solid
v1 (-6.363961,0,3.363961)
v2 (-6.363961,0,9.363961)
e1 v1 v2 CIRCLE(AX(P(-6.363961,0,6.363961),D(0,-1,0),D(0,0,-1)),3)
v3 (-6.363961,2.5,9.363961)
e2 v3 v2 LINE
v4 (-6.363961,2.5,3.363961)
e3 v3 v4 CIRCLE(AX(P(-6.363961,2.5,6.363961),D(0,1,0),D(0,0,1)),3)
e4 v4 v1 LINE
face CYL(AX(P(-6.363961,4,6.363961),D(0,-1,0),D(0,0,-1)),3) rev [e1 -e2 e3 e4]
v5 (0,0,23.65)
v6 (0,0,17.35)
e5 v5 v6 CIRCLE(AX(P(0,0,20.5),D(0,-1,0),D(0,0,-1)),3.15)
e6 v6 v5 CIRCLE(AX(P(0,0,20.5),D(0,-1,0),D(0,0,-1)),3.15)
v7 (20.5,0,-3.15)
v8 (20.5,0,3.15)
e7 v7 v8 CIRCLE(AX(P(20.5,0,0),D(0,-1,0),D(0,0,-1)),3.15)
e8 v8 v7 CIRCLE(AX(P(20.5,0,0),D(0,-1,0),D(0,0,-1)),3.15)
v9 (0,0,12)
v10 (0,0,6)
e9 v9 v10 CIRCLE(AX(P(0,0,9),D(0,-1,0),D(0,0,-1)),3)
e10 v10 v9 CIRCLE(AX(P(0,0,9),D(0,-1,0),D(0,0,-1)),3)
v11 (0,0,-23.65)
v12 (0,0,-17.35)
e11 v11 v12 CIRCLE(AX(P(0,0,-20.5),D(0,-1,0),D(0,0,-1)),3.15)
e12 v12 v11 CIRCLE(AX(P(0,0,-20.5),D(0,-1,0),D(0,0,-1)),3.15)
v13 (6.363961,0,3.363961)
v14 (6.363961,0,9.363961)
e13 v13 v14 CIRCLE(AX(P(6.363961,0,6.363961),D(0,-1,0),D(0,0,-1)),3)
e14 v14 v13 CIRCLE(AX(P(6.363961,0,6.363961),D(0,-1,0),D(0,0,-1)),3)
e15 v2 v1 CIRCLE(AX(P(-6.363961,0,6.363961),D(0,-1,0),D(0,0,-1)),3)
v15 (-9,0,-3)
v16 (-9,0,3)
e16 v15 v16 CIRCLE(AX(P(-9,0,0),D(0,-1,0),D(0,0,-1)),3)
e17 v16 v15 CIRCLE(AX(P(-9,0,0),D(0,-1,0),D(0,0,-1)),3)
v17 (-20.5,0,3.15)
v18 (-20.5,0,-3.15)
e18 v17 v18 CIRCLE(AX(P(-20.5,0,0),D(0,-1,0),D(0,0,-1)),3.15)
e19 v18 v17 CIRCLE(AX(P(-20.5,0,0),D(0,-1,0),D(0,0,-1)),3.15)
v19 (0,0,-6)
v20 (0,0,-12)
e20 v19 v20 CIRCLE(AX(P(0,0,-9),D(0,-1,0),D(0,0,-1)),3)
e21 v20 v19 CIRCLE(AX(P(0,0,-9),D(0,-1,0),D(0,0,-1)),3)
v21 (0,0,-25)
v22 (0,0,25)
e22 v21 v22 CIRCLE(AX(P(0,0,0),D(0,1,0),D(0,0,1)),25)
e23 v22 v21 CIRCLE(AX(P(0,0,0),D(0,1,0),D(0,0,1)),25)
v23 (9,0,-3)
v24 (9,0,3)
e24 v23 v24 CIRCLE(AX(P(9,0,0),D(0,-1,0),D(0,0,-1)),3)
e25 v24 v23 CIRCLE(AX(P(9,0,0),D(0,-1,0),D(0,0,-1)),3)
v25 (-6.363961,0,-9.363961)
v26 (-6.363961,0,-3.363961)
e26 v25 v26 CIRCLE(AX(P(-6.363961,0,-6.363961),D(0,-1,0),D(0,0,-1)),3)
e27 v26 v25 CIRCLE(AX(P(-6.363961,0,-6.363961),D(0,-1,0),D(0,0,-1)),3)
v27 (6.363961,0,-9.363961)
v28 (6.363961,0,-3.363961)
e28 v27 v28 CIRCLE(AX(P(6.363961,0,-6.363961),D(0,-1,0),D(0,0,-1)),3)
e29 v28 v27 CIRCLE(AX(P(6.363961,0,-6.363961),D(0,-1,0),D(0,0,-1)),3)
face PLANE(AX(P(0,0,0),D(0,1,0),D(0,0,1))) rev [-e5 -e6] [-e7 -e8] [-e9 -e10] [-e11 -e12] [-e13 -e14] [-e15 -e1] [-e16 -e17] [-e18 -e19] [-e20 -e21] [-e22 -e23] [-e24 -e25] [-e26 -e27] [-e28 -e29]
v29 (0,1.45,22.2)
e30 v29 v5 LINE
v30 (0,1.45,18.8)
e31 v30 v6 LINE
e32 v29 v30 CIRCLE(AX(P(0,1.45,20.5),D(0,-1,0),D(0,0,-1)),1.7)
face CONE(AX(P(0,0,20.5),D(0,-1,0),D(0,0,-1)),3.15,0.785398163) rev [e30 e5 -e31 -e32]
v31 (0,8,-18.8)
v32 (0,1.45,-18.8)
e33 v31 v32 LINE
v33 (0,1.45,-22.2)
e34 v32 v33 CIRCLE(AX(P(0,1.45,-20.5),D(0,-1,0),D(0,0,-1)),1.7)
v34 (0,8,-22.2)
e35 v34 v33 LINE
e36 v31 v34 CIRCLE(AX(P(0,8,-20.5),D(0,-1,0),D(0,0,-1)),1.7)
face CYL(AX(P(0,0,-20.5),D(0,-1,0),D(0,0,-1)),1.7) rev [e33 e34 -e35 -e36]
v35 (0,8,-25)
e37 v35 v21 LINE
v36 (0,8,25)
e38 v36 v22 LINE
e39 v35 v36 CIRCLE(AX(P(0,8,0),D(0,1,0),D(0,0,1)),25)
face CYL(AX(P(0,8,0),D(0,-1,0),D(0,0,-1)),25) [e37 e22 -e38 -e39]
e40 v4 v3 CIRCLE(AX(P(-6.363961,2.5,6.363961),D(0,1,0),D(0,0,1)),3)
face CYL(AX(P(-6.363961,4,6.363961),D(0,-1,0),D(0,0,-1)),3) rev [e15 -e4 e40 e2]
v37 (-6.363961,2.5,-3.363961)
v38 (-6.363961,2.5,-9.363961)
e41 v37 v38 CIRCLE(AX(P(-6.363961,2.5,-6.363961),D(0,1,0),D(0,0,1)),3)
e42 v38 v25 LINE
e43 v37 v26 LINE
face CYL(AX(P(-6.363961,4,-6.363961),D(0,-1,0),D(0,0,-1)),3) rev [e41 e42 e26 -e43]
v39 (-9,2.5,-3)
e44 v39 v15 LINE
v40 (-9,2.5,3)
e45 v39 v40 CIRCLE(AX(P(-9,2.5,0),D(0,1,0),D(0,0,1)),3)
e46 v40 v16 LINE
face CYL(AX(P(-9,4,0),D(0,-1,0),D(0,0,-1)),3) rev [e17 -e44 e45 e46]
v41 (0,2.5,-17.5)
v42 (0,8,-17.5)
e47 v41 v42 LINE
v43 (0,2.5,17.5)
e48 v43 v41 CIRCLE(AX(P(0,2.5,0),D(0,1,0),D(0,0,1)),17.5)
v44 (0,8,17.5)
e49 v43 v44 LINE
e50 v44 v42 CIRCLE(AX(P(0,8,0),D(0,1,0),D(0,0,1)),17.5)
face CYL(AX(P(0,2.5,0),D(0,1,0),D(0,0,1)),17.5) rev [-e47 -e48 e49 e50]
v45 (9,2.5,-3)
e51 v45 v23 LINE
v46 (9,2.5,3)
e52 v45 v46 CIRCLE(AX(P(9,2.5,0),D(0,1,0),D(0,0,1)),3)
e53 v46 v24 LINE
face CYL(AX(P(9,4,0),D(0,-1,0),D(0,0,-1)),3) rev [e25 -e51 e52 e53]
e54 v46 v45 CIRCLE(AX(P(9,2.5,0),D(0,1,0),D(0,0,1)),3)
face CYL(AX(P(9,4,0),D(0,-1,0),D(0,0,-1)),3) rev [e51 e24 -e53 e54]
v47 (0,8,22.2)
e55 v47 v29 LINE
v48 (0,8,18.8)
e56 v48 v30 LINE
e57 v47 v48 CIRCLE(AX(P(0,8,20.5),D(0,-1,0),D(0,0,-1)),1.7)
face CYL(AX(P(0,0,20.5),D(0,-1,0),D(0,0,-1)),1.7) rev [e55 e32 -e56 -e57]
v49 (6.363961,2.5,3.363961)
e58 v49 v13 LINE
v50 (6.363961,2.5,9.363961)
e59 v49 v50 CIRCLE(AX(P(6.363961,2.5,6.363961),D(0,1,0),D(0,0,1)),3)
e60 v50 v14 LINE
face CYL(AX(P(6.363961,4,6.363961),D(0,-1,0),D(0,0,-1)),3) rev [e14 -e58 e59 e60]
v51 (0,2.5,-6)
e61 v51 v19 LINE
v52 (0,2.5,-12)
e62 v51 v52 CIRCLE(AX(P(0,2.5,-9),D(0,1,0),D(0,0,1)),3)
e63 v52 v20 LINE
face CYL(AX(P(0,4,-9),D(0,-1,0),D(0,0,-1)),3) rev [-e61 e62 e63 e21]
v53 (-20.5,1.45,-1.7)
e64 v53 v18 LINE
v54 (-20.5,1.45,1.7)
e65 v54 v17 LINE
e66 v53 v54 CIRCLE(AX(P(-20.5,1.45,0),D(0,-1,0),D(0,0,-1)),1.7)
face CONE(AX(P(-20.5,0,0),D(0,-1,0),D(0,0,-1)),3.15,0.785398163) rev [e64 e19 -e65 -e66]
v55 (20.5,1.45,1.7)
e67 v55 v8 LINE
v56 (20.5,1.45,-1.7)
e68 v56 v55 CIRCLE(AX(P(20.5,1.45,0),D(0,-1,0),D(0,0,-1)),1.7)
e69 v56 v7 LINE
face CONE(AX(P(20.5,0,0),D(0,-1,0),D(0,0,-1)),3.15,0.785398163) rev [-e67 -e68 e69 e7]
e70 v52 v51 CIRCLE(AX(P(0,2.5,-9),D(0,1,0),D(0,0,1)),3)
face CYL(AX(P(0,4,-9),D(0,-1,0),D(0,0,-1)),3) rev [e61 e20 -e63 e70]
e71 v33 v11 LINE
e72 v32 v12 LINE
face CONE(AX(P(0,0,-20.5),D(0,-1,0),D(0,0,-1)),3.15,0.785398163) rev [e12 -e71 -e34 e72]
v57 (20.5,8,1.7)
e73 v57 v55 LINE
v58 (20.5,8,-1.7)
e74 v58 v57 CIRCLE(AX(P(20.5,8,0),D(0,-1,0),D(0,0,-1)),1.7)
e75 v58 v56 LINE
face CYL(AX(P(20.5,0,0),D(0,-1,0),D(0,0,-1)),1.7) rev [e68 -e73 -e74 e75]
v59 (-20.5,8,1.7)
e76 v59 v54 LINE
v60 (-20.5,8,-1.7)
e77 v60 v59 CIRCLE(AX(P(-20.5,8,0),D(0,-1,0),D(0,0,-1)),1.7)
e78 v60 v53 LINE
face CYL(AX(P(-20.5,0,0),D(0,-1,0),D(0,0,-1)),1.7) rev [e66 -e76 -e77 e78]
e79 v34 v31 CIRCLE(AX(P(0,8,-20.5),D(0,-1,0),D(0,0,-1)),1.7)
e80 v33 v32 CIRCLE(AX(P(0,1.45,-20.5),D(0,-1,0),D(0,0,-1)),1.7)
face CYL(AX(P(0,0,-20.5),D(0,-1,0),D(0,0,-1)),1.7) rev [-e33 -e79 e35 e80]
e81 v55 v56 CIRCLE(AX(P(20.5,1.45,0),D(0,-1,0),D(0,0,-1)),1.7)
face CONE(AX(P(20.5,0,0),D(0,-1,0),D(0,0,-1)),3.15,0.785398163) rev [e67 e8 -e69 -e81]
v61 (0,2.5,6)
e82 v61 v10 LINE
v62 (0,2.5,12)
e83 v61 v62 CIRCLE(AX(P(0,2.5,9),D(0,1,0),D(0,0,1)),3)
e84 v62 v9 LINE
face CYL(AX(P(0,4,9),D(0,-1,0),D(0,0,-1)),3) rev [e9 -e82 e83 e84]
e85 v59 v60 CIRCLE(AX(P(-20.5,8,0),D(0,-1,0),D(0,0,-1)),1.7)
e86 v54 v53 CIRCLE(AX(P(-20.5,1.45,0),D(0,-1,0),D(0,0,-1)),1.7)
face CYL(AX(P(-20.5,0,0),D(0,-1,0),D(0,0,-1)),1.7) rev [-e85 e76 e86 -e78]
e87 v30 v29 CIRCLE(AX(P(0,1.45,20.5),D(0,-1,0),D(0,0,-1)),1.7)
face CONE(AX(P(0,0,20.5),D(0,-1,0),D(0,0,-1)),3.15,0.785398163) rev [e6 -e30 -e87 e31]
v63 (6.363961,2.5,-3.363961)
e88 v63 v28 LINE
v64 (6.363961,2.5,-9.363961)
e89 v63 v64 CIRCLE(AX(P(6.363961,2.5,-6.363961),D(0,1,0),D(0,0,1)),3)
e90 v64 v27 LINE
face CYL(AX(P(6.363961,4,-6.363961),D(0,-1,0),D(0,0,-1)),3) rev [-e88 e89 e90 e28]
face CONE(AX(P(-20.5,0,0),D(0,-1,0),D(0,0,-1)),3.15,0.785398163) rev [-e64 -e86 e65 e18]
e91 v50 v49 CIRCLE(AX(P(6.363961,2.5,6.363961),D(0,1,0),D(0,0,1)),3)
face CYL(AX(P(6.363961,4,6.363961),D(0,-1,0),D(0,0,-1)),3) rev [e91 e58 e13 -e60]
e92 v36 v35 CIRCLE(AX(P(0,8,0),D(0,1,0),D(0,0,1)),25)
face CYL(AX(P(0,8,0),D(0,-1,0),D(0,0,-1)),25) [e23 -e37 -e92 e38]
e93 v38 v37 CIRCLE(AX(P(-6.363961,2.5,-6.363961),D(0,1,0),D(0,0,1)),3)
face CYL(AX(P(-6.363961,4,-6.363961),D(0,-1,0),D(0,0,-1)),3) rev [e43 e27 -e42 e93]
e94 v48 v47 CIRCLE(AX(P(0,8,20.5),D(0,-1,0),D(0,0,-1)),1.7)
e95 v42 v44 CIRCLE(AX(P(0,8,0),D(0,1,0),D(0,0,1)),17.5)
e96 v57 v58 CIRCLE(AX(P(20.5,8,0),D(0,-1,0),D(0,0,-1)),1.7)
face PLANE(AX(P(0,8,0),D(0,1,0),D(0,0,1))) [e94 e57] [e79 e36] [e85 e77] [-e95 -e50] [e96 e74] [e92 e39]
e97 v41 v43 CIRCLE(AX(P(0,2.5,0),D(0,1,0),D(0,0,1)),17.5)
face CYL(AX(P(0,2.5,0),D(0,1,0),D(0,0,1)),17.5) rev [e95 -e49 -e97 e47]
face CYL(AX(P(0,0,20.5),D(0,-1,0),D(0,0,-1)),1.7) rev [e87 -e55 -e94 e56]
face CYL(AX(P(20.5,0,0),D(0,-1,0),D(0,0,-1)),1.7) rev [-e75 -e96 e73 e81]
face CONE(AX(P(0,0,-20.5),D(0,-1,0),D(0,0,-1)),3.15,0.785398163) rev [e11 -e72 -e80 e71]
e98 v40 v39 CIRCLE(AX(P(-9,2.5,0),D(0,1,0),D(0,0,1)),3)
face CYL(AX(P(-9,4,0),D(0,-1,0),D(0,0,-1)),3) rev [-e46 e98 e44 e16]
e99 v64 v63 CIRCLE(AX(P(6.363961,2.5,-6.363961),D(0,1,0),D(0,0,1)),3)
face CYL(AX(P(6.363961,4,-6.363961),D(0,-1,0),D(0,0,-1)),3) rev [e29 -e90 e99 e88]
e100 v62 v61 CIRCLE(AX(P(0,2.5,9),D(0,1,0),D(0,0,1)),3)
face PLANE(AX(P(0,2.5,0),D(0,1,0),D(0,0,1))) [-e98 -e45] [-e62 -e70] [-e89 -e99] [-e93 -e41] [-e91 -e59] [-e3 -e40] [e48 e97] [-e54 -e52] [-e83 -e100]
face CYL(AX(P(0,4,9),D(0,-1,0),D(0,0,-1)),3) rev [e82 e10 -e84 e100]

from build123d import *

# Parameters (mm, degrees)
SKETCH1_R                                       = 25
BOSS_EXTRUDE1_DEPTH                             = 8
SKETCH2_R                                       = 17.5
CUT_EXTRUDE1_DEPTH                              = 5.5
SKETCH3_R                                       = 3
CUT_EXTRUDE2_DEPTH                              = 4
CSK_FOR_M3_FLAT_HEAD_MACHINE_SCREW1_D           = 3.4
CSK_FOR_M3_FLAT_HEAD_MACHINE_SCREW1_CSINK_D     = 6.3
CSK_FOR_M3_FLAT_HEAD_MACHINE_SCREW1_CSINK_ANGLE = 90


with BuildPart() as part:
    # Sketch1 → Boss-Extrude1 (new body)
    with BuildSketch(Plane(origin=(0, 0, 0), x_dir=(1, 0, 0), z_dir=(0, 1, 0))):
        with Locations(Location((0, 0, 0), (0, 0, 270))):
            Circle(SKETCH1_R)
    extrude(amount=BOSS_EXTRUDE1_DEPTH)

    # Sketch2 → Cut-Extrude1 (cut)
    with BuildSketch(Plane(origin=(0, 8, 0), x_dir=(1, 0, 0), z_dir=(0, 1, 0))):
        with Locations(Location((0, 0, 0), (0, 0, 270))):
            Circle(SKETCH2_R)
    extrude(amount=-CUT_EXTRUDE1_DEPTH, mode=Mode.SUBTRACT)

    # Sketch3 → Cut-Extrude2 (cut)
    with BuildSketch(Plane.XZ):
        with Locations(Location((0, -9, 0), (0, 0, 270))):
            Circle(SKETCH3_R)
        with Locations(Location((-6.363961031, -6.363961031, 0), (0, 0, 270))):
            Circle(SKETCH3_R)
        with Locations(Location((-9, 0, 0), (0, 0, 270))):
            Circle(SKETCH3_R)
        with Locations(Location((-6.363961031, 6.363961031, 0), (0, 0, 270))):
            Circle(SKETCH3_R)
        with Locations(Location((0, 9, 0), (0, 0, 270))):
            Circle(SKETCH3_R)
        with Locations(Location((6.363961031, 6.363961031, 0), (0, 0, 270))):
            Circle(SKETCH3_R)
        with Locations(Location((9, 0, 0), (0, 0, 270))):
            Circle(SKETCH3_R)
        with Locations(Location((6.363961031, -6.363961031, 0), (0, 0, 270))):
            Circle(SKETCH3_R)
    extrude(amount=-CUT_EXTRUDE2_DEPTH, mode=Mode.SUBTRACT)

    # CSK for M3 Flat Head Machine Screw1 (through all)
    with Locations(Plane(origin=(0, 0, 0), x_dir=(-1, 0, 0), z_dir=(0, -1, 0))):
        with Locations((20.5, 0), (0, 20.5), (-20.5, 0), (0, -20.5)):
            CounterSinkHole(CSK_FOR_M3_FLAT_HEAD_MACHINE_SCREW1_D / 2, CSK_FOR_M3_FLAT_HEAD_MACHINE_SCREW1_CSINK_D / 2, counter_sink_angle=CSK_FOR_M3_FLAT_HEAD_MACHINE_SCREW1_CSINK_ANGLE)


solid = part.part
